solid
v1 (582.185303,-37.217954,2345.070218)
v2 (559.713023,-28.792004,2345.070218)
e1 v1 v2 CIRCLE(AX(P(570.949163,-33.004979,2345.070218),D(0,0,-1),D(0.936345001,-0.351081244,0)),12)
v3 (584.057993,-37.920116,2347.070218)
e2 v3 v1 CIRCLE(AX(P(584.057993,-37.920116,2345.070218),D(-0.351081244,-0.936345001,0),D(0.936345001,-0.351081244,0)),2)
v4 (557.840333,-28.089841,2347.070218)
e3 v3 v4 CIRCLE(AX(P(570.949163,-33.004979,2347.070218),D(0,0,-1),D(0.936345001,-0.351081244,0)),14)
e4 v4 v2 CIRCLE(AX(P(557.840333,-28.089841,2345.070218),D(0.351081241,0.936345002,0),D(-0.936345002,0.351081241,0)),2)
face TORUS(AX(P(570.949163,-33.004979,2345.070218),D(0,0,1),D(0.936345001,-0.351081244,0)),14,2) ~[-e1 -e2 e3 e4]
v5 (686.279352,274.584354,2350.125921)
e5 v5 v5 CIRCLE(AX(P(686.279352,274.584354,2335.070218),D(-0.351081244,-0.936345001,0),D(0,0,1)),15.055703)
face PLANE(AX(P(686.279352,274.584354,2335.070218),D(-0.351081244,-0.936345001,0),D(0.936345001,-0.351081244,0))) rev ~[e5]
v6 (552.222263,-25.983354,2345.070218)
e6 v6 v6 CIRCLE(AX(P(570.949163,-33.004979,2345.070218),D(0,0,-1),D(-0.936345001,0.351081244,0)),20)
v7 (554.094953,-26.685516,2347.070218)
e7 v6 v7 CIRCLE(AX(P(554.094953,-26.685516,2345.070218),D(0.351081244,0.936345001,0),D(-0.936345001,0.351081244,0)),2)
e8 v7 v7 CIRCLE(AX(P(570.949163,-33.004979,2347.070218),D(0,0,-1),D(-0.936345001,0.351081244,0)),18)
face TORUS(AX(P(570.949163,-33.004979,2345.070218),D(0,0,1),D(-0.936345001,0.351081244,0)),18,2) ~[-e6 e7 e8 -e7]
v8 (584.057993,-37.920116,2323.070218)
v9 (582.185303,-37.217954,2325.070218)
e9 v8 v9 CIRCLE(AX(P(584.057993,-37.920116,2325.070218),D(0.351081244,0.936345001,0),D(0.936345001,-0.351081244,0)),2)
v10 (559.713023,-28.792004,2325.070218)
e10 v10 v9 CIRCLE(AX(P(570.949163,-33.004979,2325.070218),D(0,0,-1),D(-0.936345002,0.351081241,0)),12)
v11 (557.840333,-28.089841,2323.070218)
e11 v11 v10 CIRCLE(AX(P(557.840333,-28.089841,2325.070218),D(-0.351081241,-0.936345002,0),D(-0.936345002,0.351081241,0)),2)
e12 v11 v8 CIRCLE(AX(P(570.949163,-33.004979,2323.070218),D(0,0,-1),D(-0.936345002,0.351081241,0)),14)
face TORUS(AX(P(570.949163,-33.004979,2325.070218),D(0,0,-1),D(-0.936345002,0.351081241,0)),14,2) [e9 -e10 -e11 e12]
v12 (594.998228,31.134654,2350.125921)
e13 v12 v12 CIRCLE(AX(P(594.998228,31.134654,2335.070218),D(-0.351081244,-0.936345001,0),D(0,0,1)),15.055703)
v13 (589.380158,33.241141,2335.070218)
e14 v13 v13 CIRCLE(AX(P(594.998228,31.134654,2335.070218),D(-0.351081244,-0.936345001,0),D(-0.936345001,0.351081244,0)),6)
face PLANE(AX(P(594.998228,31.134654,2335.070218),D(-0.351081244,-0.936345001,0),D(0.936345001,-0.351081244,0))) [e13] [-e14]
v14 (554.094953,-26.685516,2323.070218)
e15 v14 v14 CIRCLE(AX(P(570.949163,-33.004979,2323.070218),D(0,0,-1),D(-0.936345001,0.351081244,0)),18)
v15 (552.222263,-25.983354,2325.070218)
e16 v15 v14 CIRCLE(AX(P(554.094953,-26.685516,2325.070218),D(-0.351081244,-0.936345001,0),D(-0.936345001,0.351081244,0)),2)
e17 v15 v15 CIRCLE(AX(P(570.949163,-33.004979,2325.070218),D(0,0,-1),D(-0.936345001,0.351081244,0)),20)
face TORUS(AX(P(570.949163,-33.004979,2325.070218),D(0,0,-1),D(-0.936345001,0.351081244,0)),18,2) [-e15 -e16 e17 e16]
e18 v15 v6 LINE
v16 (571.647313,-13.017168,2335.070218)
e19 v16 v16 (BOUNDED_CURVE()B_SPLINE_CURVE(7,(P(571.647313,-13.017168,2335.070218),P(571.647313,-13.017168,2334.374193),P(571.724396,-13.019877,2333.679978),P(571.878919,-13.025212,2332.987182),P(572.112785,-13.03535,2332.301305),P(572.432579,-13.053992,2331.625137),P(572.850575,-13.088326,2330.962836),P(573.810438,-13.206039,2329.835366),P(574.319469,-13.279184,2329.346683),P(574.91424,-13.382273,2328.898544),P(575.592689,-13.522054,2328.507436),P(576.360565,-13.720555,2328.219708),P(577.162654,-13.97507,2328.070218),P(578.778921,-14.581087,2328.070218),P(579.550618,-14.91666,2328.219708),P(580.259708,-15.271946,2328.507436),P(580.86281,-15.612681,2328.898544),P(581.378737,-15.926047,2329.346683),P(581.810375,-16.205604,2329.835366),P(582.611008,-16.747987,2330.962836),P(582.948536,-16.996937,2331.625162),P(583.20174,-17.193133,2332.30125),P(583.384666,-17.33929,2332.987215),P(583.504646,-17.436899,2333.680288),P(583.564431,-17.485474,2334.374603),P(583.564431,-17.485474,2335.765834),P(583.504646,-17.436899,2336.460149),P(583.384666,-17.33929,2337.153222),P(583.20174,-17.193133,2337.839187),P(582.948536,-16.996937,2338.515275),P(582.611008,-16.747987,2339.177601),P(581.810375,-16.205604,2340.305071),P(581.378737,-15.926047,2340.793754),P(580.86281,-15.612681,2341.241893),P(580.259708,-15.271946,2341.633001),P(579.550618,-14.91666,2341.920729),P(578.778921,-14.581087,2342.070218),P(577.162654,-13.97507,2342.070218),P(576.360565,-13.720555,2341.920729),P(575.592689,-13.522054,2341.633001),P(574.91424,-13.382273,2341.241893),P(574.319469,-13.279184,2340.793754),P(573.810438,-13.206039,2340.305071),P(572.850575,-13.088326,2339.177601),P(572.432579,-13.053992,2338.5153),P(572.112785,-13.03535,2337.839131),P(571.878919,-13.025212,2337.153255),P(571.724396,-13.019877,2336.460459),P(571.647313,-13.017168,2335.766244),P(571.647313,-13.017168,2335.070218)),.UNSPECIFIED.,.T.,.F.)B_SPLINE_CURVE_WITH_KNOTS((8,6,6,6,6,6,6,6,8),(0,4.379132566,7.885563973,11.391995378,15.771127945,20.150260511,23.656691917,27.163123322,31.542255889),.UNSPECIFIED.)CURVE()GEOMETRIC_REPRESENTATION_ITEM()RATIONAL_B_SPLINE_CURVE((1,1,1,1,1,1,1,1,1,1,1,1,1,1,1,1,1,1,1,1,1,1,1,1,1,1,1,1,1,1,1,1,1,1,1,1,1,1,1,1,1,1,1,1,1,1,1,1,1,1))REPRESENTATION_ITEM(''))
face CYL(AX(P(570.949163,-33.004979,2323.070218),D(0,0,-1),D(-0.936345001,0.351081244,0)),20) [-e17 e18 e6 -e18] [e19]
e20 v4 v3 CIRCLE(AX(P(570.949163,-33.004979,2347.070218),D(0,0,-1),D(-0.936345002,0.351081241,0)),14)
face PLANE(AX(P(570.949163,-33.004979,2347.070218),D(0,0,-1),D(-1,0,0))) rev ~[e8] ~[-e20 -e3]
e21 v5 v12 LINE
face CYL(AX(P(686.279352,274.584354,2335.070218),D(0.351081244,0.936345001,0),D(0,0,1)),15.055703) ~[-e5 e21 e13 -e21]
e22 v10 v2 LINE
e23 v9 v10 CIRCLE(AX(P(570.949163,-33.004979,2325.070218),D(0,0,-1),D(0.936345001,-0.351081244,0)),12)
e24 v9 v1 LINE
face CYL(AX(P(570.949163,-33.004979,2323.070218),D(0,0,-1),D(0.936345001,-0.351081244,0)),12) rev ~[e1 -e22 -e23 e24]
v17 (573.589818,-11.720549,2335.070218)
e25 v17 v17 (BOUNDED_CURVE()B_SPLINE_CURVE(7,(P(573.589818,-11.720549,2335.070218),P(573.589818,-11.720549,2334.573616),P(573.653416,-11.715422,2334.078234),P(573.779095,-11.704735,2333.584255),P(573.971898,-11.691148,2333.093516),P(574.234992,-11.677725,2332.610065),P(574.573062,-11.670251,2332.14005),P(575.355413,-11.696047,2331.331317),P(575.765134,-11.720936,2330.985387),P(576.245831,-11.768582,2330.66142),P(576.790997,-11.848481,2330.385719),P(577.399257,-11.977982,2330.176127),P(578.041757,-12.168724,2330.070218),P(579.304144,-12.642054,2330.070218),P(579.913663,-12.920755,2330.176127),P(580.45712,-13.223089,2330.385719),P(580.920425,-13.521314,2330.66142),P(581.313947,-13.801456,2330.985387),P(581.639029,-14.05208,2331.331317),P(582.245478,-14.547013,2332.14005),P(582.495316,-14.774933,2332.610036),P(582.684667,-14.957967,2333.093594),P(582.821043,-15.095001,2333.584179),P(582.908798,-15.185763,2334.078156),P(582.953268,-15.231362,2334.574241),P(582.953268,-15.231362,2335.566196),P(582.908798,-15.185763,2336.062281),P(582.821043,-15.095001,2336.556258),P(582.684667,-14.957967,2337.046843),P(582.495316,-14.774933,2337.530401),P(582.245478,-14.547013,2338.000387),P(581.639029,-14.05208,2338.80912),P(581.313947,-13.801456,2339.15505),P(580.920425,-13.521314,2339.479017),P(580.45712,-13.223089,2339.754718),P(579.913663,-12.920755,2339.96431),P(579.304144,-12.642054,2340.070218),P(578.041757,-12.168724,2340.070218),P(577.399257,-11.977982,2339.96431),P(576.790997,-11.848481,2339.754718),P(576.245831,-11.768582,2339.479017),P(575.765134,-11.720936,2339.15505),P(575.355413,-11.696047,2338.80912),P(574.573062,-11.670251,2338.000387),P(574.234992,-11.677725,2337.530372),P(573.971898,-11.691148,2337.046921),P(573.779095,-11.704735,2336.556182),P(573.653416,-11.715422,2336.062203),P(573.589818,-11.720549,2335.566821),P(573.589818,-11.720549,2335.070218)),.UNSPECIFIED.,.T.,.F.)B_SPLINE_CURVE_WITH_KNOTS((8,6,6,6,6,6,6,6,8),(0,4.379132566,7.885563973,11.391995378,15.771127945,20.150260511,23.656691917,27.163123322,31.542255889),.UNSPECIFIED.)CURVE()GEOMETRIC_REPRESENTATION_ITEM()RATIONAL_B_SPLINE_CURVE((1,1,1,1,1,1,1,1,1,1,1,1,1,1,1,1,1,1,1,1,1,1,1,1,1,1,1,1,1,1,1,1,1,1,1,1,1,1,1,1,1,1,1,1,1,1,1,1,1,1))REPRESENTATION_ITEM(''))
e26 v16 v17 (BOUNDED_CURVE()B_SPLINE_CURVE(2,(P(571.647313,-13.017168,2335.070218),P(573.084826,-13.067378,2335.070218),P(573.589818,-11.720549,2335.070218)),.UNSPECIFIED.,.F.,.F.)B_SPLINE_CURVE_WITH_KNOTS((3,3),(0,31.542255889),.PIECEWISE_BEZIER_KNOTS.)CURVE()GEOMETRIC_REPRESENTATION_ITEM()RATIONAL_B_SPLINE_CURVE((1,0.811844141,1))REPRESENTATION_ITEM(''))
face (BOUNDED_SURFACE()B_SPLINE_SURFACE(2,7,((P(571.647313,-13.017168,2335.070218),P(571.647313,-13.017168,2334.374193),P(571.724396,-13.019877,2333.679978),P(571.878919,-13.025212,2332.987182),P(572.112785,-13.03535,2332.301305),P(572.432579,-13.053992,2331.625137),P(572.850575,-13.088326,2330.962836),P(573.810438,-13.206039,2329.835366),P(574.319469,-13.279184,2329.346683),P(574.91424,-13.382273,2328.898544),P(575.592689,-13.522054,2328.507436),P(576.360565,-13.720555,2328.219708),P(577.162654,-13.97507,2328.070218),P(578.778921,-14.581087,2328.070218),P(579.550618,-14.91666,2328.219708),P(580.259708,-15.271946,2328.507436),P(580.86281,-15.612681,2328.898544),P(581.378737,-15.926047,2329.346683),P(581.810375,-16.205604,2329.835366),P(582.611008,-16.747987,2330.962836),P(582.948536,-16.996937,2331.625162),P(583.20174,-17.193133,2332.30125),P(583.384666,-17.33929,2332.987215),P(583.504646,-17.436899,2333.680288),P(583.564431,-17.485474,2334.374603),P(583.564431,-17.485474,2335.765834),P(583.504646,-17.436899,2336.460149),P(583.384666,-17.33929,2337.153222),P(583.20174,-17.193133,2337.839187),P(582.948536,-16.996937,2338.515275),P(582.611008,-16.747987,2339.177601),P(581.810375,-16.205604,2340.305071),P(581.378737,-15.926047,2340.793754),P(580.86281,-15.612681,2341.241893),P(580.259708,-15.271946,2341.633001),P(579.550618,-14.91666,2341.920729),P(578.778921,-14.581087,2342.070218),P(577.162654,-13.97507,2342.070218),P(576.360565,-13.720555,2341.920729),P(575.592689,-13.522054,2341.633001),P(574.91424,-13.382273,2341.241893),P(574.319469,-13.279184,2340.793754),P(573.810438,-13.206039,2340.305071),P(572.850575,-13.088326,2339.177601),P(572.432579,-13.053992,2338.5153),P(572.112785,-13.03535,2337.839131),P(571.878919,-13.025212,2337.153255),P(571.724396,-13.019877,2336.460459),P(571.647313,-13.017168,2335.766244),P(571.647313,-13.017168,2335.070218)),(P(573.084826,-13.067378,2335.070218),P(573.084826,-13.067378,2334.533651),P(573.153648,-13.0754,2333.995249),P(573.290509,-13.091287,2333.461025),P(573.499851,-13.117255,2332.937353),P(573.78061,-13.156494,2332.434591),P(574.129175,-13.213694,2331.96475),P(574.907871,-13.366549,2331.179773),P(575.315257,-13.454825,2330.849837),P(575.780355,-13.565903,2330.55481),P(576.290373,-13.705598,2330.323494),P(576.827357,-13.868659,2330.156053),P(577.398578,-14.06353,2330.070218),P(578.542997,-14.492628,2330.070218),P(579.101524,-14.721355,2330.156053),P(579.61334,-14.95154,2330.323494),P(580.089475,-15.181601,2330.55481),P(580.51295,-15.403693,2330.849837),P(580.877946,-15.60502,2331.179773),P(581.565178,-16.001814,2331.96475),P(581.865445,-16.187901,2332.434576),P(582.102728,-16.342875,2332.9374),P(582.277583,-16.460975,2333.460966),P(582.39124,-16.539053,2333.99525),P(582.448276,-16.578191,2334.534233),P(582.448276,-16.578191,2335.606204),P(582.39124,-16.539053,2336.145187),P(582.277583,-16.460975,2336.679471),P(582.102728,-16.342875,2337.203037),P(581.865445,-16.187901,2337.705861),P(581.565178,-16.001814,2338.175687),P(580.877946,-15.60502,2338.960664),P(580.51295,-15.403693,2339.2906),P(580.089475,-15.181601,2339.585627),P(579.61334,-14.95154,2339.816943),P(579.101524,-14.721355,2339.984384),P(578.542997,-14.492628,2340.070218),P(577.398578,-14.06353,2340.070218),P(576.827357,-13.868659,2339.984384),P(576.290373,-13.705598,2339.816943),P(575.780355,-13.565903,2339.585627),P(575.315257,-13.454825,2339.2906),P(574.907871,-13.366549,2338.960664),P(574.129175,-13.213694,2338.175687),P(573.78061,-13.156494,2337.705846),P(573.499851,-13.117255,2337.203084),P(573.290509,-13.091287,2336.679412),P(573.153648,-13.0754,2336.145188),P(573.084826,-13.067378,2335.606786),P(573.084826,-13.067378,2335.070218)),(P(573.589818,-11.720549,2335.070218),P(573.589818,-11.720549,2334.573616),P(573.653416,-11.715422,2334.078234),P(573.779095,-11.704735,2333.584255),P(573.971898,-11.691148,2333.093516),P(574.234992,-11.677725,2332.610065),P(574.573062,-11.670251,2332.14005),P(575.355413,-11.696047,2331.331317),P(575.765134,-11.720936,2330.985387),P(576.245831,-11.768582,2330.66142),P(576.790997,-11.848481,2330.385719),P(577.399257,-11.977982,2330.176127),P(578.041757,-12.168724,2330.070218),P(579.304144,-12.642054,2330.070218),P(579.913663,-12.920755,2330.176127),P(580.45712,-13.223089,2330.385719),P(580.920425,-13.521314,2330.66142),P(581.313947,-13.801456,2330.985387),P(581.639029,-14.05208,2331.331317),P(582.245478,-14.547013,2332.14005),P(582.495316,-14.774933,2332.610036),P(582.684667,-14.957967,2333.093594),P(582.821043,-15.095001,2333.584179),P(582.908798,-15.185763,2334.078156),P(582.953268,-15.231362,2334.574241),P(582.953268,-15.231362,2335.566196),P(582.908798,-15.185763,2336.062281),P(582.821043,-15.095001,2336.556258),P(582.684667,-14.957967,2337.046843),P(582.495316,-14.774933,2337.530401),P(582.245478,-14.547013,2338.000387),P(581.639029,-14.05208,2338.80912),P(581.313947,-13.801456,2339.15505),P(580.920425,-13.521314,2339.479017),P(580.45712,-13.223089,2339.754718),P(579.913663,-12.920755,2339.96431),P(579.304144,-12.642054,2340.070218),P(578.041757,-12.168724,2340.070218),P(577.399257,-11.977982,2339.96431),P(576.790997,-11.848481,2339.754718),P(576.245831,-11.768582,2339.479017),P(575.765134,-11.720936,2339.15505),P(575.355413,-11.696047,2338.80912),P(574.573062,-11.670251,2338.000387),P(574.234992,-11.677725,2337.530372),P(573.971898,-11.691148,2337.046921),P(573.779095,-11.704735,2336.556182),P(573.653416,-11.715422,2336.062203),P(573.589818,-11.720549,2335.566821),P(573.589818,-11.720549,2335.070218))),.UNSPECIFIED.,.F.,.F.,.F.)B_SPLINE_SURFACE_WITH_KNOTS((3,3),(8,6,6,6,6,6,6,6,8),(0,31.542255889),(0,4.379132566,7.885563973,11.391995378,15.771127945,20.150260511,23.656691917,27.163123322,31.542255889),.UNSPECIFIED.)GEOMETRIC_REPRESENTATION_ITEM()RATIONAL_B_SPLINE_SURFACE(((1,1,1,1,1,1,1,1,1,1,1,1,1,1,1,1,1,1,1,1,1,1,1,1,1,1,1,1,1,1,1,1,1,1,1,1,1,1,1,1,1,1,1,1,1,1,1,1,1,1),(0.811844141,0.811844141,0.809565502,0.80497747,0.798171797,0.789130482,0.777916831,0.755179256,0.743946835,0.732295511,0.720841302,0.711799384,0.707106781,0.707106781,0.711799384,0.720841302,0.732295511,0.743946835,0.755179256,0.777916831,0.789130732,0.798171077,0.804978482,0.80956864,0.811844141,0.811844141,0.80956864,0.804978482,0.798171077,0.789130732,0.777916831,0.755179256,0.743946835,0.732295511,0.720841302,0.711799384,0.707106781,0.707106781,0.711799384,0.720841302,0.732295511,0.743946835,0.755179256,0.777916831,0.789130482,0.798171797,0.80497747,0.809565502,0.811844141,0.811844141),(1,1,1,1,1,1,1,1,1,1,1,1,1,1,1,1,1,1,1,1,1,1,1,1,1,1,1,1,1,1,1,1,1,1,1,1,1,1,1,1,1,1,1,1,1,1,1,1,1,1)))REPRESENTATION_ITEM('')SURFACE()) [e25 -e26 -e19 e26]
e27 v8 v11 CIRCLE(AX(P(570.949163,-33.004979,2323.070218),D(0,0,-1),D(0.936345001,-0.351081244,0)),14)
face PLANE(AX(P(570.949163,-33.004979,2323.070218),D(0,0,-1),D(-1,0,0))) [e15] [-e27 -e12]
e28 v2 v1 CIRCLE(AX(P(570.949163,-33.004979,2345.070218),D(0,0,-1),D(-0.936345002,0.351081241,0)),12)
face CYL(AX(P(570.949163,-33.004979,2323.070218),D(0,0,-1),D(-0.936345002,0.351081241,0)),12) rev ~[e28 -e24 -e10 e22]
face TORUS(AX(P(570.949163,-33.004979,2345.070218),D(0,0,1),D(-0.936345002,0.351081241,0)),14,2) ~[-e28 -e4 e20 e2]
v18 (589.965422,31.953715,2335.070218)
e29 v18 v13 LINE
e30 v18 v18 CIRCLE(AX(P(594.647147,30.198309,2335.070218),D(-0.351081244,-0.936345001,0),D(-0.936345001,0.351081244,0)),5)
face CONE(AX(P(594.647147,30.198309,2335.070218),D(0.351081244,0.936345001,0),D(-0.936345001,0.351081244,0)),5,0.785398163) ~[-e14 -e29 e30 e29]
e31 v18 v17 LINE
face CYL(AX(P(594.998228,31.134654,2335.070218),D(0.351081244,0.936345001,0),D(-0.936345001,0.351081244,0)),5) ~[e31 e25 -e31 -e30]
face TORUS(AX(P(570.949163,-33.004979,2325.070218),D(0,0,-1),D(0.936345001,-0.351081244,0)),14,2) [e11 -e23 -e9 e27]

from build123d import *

# Parameters (mm, degrees)
BOSS_EXTRUDE1_START      = -260
BOSS_EXTRUDE1_DEPTH      = 260
BOSS_EXTRUDE4_DEPTH      = 24
BOSS_EXTRUDE5_REACH      = 2447.334
BOSS_EXTRUDE5_END_RADIUS = 20
SKETCH5_R                = 5
FILLET1_R                = 2
FILLET2_R                = 2
CHAMFER2_SIZE            = 1


with BuildPart() as part:
    # Sketch1 → Boss-Extrude1 (new body)
    with BuildSketch(Plane(origin=(83.573308801, 222.892709782, 0), x_dir=(0.9363450005078556, -0.3510812441927706, 0), z_dir=(-0.3510812441927706, -0.9363450005078556, 0)).offset(BOSS_EXTRUDE1_START)):
        with BuildLine():
            ThreePointArc((546.192823225, 2320.014515708), (561.248526003, 2335.070218486), (546.192823225, 2350.125921264))
            ThreePointArc((546.192823225, 2350.125921264), (531.137120447, 2335.070218486), (546.192823225, 2320.014515708))
        make_face()
    extrude(amount=BOSS_EXTRUDE1_DEPTH)



with BuildPart() as body_2:
    # Sketch6 → Boss-Extrude4 (new body)
    with BuildSketch(Plane(origin=(0, 0, 2323.070218486), x_dir=(-1, 0, 0), z_dir=(0, 0, -1))):
        with BuildLine():
            ThreePointArc((-589.676062924, -40.026603584), (-563.92753803, -51.73187871), (-552.222262904, -25.983353816))
            ThreePointArc((-552.222262904, -25.983353816), (-577.970787798, -14.27807869), (-589.676062924, -40.026603584))
        make_face()
        with BuildLine():
            ThreePointArc((-582.18530292, -37.21795363), (-566.736188003, -44.241118713), (-559.713022893, -28.792003808))
            ThreePointArc((-559.713022893, -28.792003808), (-575.162137825, -21.768838687), (-582.18530292, -37.21795363))
        make_face(mode=Mode.SUBTRACT)
    extrude(amount=-BOSS_EXTRUDE4_DEPTH)


with BuildPart() as part_1:
    add(part.part)

    add(body_2.part)  # Boss-Extrude5 merges body 2
    # Boss-Extrude5: up to this cylinder (the profile starts outside it)
    boss_extrude5_end = Plane(origin=(570.949162914, -33.0049787, 2335.070218), z_dir=(0, 0, -1)) * Cylinder(BOSS_EXTRUDE5_END_RADIUS, 4935.668, mode=Mode.PRIVATE)
    # Sketch5 → Boss-Extrude5 (add, up to the surface)
    with BuildSketch(Plane(origin=(83.573308801, 222.892709782, 0), x_dir=(0.9363450005078556, -0.3510812441927706, 0), z_dir=(-0.3510812441927706, -0.9363450005078556, 0)), mode=Mode.PRIVATE) as boss_extrude5_sk1:
        with Locations(Location((546.192823225, 2335.070218486, 0), (0, 0, 180))):
            Circle(SKETCH5_R)
    boss_extrude5_tool1 = extrude(boss_extrude5_sk1.sketch, amount=BOSS_EXTRUDE5_REACH, mode=Mode.PRIVATE) - boss_extrude5_end
    add(boss_extrude5_tool1.solids().sort_by_distance((594.998228, 31.134654, 2335.070218))[0])

    # Fillet1
    fillet1_edges = [part_1.edges().sort_by_distance(p)[0] for p in [
        (582.429546976, -16.628141955, 2335.070218486),
    ]]
    fillet(fillet1_edges, radius=FILLET1_R)

    # Fillet2
    fillet2_edges = [part_1.edges().sort_by_distance(p)[0] for p in [
        (559.713022908, -28.79200377, 2347.070218486),
        (589.676062924, -40.026603584, 2347.070218486),
        (559.713022908, -28.79200377, 2323.070218486),
        (589.676062924, -40.026603584, 2323.070218486),
    ]]
    fillet(fillet2_edges, radius=FILLET2_R)

    # Chamfer2
    chamfer2_edges = [part_1.edges().sort_by_distance(p)[0] for p in [
        (599.679953144, 29.379247614, 2335.070218486),
    ]]
    chamfer(chamfer2_edges, length=CHAMFER2_SIZE)


solid = part_1.part
